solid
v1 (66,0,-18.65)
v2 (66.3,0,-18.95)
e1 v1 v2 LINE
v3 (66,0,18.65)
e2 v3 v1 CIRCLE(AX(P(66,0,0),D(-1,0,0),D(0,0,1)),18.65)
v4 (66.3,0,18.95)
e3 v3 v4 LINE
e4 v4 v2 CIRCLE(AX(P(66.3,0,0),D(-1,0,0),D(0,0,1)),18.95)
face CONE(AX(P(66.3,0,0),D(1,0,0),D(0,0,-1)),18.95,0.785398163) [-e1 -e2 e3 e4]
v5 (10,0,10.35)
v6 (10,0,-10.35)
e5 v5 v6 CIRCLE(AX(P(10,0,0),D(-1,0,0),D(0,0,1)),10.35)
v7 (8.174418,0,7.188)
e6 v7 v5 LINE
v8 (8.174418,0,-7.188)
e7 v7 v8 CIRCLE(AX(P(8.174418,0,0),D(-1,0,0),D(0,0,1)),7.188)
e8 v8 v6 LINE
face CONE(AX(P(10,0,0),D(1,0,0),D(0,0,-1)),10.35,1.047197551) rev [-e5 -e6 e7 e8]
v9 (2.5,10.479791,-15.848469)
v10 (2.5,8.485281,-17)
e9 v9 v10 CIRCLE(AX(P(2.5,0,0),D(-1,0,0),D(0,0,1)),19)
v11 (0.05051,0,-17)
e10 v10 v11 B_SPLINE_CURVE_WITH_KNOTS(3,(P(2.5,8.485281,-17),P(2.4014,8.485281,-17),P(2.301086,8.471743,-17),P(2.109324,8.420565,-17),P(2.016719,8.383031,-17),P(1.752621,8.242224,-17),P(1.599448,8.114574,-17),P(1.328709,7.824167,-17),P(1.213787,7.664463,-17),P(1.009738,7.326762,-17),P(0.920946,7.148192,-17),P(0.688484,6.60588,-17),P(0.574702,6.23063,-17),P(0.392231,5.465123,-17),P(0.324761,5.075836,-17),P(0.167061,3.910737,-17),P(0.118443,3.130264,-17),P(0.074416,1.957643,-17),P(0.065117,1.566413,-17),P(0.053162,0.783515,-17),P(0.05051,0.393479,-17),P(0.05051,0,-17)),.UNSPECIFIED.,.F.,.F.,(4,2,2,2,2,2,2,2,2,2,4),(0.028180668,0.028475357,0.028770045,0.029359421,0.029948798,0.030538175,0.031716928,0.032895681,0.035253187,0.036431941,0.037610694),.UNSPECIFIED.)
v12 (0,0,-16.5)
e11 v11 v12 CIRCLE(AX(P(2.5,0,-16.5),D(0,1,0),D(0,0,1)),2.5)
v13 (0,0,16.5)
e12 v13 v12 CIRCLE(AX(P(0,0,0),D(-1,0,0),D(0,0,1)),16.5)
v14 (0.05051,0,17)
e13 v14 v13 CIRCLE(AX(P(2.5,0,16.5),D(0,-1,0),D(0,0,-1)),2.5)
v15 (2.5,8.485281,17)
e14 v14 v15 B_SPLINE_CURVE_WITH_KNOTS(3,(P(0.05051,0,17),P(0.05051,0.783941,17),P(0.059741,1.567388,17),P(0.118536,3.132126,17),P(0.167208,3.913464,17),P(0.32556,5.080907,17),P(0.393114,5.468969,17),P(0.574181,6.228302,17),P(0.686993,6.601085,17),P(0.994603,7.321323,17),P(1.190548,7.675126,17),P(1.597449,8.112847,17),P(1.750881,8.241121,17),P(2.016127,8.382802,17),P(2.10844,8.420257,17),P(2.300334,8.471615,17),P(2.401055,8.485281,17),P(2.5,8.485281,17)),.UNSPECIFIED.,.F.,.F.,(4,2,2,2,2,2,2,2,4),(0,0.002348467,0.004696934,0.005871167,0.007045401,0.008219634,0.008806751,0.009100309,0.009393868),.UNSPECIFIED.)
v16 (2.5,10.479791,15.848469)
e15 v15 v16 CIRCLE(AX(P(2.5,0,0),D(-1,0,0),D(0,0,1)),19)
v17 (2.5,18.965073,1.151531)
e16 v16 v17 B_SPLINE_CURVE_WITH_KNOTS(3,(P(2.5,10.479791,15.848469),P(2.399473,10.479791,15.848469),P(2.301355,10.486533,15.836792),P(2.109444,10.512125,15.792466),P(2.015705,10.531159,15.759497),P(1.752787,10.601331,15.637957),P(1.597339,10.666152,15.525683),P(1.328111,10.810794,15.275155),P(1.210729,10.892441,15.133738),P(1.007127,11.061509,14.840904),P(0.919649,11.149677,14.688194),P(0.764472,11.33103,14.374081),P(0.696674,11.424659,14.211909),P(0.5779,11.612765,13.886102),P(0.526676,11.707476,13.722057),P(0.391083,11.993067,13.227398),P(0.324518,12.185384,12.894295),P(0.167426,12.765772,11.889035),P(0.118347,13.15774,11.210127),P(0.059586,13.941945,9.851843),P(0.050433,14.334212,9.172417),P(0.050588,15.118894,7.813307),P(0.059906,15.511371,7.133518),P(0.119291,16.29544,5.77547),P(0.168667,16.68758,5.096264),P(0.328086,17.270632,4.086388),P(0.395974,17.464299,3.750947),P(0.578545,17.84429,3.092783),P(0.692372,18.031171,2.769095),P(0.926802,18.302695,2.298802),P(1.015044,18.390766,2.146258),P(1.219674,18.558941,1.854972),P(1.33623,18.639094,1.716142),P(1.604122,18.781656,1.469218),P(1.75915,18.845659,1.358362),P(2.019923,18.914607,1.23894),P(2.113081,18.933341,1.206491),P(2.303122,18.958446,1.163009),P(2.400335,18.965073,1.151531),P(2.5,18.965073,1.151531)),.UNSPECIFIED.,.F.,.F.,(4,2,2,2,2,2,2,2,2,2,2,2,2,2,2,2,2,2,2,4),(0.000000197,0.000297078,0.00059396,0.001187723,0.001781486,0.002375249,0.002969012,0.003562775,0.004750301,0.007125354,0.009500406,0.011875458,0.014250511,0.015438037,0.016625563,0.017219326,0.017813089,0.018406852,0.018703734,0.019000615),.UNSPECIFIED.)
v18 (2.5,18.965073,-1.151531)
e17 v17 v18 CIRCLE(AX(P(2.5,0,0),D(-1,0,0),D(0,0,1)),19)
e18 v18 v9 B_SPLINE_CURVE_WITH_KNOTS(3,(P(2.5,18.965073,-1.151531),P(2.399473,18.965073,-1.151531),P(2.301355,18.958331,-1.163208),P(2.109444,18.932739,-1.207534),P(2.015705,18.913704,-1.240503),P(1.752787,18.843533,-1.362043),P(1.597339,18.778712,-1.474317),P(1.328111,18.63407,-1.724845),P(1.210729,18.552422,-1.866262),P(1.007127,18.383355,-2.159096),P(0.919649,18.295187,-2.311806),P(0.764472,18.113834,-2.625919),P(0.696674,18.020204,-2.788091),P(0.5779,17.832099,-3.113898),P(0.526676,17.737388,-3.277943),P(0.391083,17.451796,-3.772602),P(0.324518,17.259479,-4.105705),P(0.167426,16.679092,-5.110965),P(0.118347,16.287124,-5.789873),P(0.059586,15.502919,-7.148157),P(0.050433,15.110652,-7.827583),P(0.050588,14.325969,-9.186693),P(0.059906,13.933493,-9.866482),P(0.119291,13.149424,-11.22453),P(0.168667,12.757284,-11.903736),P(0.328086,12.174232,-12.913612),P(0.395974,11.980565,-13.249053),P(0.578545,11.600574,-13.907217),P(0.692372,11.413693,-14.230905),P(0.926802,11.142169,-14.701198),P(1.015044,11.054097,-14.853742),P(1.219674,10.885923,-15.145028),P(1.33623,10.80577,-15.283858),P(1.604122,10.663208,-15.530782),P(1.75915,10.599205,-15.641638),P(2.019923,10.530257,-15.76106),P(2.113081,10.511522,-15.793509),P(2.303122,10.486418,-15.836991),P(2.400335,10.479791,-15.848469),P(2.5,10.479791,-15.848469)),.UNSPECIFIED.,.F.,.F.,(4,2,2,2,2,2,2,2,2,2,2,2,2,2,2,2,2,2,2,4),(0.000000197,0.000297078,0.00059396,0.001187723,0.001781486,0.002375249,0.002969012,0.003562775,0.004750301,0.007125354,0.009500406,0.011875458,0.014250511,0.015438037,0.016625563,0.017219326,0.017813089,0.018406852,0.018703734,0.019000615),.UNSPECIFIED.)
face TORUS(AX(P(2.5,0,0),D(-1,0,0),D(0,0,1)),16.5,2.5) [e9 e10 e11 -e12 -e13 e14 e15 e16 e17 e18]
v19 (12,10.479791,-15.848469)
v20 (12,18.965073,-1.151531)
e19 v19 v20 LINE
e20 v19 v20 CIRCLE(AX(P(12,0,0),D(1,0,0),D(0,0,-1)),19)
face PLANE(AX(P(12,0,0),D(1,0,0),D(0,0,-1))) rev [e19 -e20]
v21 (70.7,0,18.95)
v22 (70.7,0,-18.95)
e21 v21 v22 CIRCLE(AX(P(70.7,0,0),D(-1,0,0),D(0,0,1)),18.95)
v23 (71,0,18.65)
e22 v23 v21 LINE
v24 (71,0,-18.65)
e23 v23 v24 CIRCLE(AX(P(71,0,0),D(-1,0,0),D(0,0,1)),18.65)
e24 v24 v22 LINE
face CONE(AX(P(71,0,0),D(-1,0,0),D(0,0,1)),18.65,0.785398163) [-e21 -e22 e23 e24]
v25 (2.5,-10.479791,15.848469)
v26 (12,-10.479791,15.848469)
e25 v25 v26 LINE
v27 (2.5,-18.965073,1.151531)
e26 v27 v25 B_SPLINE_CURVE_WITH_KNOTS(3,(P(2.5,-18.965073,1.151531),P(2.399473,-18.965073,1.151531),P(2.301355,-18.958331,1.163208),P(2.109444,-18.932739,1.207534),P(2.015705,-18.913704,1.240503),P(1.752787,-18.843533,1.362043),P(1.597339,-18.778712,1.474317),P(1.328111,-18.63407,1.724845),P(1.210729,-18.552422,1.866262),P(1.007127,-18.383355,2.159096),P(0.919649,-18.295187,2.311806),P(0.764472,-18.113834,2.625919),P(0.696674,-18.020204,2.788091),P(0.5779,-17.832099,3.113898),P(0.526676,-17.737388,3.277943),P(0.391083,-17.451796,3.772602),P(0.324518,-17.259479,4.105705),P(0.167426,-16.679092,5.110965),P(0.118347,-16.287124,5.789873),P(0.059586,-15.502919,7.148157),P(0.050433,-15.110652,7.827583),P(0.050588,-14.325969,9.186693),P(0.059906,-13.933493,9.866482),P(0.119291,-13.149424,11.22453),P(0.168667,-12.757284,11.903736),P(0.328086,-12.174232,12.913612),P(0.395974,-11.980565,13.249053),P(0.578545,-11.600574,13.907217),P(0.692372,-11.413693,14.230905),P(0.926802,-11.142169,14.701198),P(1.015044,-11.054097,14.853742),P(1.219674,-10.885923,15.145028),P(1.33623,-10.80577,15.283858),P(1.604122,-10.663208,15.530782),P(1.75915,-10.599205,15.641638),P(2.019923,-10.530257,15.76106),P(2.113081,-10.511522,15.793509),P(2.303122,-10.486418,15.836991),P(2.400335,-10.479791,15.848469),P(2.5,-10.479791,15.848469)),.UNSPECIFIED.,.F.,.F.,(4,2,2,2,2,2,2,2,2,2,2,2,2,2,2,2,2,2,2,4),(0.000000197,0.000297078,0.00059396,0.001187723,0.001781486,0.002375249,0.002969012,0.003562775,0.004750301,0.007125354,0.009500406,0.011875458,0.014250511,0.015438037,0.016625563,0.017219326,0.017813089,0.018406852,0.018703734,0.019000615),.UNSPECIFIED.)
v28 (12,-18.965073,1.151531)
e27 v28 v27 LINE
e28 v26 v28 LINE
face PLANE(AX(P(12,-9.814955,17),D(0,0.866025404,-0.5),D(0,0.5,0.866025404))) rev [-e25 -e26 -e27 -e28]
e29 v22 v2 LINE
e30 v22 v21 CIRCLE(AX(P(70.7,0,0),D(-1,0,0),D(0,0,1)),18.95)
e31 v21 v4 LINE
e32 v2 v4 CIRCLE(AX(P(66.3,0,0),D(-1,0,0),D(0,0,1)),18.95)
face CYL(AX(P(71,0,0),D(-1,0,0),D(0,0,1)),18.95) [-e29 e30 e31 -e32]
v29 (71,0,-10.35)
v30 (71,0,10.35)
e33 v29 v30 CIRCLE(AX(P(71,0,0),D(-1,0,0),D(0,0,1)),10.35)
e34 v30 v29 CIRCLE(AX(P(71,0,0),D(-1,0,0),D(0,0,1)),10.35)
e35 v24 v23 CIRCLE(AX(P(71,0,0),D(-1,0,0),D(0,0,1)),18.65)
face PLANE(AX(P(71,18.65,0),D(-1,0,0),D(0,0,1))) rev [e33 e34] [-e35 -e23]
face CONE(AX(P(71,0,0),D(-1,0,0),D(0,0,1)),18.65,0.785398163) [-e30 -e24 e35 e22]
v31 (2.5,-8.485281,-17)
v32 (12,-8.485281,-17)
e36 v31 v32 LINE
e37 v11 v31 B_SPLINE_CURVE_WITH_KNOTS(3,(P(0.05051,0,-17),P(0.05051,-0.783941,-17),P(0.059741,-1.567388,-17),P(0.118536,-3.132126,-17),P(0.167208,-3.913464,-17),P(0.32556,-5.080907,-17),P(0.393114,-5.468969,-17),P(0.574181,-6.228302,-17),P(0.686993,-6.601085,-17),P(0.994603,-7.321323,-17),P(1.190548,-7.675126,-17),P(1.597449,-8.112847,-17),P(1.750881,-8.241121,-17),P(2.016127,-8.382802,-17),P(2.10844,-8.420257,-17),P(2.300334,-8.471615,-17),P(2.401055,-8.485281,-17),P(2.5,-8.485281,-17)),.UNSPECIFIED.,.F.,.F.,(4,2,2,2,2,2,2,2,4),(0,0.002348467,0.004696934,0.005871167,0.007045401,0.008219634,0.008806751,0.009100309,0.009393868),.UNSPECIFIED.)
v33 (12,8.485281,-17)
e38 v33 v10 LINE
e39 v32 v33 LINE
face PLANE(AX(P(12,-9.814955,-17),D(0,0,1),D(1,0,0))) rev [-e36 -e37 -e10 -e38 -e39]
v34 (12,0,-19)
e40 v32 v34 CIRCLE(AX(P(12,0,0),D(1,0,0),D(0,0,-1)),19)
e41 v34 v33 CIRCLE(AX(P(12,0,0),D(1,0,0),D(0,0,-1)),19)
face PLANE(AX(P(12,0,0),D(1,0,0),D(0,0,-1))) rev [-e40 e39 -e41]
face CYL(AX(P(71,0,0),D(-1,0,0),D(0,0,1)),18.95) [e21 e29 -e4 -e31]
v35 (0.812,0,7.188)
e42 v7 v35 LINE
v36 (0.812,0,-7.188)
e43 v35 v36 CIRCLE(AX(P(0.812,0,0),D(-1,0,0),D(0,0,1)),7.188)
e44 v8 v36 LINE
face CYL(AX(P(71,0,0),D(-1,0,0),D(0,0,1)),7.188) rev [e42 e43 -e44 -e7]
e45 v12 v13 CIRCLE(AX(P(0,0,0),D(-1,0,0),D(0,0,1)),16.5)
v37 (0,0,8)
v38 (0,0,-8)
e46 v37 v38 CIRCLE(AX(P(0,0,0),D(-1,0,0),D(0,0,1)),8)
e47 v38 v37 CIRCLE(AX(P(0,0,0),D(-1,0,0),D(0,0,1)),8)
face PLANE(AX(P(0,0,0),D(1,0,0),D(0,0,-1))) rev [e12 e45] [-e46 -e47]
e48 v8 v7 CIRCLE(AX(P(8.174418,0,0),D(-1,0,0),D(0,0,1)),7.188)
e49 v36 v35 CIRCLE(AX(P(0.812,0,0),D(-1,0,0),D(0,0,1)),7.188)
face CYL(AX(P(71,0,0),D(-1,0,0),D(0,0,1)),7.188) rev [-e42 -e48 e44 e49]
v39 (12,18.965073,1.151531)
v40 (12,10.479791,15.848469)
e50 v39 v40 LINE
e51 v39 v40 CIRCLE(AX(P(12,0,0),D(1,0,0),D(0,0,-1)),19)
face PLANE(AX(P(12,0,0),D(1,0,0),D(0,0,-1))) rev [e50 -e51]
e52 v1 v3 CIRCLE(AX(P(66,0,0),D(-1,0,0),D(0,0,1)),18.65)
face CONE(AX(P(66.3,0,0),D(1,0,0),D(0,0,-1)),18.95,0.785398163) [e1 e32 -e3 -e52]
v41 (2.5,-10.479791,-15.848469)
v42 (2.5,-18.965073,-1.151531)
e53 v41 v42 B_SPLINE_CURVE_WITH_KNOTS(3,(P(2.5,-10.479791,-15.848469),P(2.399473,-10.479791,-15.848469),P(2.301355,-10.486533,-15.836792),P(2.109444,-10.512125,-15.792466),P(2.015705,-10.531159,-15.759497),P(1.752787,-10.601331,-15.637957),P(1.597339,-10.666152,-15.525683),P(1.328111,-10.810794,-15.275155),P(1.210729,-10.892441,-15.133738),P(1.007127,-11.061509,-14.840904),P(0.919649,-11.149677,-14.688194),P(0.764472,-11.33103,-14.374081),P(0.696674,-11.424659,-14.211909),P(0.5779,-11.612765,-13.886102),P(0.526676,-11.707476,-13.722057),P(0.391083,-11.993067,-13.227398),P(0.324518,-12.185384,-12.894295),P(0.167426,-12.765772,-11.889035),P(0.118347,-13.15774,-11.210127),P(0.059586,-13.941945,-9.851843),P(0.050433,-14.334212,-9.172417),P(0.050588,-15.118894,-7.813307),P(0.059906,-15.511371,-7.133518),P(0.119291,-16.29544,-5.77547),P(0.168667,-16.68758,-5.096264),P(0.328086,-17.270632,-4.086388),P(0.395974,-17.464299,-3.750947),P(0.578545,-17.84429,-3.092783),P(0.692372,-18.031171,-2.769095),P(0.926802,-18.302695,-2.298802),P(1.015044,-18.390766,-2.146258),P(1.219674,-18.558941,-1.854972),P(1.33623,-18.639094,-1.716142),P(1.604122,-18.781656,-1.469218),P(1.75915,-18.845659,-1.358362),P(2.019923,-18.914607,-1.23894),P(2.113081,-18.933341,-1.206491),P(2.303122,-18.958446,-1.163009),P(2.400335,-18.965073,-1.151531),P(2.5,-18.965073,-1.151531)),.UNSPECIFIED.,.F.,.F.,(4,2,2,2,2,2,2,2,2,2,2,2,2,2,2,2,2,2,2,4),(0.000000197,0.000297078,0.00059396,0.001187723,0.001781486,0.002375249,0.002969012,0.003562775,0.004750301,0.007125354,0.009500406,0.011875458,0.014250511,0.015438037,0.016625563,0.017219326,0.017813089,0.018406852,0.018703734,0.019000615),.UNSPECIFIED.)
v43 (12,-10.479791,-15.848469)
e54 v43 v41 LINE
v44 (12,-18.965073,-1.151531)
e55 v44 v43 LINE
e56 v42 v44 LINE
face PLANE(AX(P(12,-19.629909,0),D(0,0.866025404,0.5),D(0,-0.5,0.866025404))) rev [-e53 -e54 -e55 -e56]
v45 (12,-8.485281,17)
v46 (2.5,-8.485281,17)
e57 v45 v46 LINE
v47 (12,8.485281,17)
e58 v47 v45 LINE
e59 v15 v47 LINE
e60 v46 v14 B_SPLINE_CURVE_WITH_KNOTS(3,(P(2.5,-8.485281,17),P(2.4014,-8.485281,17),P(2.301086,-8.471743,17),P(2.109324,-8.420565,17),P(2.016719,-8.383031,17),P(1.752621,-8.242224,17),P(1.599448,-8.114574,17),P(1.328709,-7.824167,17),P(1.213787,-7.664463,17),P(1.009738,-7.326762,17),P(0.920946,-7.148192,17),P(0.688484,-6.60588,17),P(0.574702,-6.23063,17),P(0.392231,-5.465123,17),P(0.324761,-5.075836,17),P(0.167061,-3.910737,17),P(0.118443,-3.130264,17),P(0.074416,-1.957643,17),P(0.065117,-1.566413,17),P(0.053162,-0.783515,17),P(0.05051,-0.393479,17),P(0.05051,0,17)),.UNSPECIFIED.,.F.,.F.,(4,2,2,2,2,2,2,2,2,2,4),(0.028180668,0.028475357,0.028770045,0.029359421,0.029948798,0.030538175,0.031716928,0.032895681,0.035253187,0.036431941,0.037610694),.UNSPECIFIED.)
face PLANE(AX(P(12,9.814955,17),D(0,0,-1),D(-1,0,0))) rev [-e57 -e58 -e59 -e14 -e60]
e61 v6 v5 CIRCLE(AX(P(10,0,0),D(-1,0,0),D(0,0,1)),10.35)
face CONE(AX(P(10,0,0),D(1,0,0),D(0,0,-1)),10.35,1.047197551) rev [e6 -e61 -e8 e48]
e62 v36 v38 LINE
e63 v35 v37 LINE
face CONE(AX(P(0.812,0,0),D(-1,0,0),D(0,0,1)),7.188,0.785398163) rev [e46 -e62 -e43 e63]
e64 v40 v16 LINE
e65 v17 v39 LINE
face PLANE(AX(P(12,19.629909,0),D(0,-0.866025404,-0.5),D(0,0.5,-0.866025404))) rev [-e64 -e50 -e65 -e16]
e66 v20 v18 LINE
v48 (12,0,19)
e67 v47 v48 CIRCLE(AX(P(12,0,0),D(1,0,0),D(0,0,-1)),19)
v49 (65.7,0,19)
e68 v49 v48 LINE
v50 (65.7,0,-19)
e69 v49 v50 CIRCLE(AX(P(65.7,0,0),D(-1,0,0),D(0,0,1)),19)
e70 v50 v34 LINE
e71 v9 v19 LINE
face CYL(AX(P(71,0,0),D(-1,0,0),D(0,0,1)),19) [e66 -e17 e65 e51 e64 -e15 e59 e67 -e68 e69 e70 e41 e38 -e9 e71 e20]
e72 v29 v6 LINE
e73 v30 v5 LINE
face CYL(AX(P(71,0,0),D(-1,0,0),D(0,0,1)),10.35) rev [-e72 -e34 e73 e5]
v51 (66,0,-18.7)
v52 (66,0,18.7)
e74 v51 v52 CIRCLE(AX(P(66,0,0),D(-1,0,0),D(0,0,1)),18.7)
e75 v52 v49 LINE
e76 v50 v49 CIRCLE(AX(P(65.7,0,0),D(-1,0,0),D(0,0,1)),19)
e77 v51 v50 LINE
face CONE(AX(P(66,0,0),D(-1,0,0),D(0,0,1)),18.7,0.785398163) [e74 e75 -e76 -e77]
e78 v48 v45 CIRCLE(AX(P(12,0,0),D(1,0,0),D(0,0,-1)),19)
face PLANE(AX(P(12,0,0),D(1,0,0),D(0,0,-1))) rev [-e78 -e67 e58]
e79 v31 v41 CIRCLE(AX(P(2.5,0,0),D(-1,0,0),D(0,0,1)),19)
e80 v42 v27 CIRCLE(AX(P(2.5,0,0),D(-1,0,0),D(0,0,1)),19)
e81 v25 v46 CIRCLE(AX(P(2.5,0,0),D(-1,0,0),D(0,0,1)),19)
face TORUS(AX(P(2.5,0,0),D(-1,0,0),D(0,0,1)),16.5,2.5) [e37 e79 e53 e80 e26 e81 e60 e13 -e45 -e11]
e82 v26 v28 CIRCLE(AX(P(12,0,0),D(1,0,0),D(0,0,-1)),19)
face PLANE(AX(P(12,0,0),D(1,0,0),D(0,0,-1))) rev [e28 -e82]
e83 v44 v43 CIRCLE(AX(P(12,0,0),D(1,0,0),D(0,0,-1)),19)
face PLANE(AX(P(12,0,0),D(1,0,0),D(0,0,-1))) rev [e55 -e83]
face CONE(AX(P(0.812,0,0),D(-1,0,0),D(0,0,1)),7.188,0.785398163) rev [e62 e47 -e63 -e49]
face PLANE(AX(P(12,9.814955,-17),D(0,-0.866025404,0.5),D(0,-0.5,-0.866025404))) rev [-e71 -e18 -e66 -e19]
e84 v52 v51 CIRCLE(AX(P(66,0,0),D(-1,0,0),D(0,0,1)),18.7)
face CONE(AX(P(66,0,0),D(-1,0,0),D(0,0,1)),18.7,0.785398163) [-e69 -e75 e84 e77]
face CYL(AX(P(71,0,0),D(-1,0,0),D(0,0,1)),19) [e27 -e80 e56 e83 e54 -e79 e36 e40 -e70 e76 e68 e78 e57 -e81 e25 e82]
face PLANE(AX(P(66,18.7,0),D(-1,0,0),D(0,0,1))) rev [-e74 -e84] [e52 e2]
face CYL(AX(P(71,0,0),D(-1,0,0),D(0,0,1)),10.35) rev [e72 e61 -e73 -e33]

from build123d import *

# Parameters (mm, degrees)
SKETCH2_W          = 68
SKETCH2_H          = 68
CUT_EXTRUDE1_DEPTH = 12


with BuildPart() as part:
    # Sketch1 → Revolve1 (revolve)
    with BuildSketch(Plane.XY, mode=Mode.PRIVATE) as revolve1_sk:
        with BuildLine():
            Line((0, 0), (0, 16.5))
            ThreePointArc((0, 16.5), (0.732233047, 18.267766953), (2.5, 19))
            Line((2.5, 19), (65.7, 19))
            Line((65.7, 19), (66, 18.7))
            Line((66, 18.7), (66, 18.65))
            Line((66, 18.65), (66.3, 18.95))
            Line((66.3, 18.95), (70.7, 18.95))
            Line((70.7, 18.95), (71, 18.65))
            Line((71, 18.65), (71, 0))
            Line((71, 0), (0, 0))
        make_face()
    revolve(revolve1_sk.sketch.rotate(Axis((71, 0, 0), (-1, 0, 0)), 270), axis=Axis((71, 0, 0), (-1, 0, 0)))

    # Sketch2 → Cut-Extrude1 (cut)
    with BuildSketch(Plane(origin=(0, 0, 0), x_dir=(0, 0, -1), z_dir=(1, 0, 0))):
        Rectangle(SKETCH2_W, SKETCH2_H)
        Polygon((-17, -9.814954576), (0, -19.629909152), (17, -9.814954576), (17, 9.814954576), (0, 19.629909152), (-17, 9.814954576), align=None, mode=Mode.SUBTRACT)
    extrude(amount=CUT_EXTRUDE1_DEPTH, mode=Mode.SUBTRACT)

    # Sketch3 → Cut-Revolve1 (revolve, cut)
    with BuildSketch(Plane.XY, mode=Mode.PRIVATE) as cut_revolve1_sk:
        Polygon((0, 0), (0, 8), (0.812, 7.188), (8.174418449, 7.188), (10, 10.35), (71, 10.35), (71, 0), align=None)
    revolve(cut_revolve1_sk.sketch.rotate(Axis((71, 0, 0), (-1, 0, 0)), 270), axis=Axis((71, 0, 0), (-1, 0, 0)), mode=Mode.SUBTRACT)


solid = part.part
